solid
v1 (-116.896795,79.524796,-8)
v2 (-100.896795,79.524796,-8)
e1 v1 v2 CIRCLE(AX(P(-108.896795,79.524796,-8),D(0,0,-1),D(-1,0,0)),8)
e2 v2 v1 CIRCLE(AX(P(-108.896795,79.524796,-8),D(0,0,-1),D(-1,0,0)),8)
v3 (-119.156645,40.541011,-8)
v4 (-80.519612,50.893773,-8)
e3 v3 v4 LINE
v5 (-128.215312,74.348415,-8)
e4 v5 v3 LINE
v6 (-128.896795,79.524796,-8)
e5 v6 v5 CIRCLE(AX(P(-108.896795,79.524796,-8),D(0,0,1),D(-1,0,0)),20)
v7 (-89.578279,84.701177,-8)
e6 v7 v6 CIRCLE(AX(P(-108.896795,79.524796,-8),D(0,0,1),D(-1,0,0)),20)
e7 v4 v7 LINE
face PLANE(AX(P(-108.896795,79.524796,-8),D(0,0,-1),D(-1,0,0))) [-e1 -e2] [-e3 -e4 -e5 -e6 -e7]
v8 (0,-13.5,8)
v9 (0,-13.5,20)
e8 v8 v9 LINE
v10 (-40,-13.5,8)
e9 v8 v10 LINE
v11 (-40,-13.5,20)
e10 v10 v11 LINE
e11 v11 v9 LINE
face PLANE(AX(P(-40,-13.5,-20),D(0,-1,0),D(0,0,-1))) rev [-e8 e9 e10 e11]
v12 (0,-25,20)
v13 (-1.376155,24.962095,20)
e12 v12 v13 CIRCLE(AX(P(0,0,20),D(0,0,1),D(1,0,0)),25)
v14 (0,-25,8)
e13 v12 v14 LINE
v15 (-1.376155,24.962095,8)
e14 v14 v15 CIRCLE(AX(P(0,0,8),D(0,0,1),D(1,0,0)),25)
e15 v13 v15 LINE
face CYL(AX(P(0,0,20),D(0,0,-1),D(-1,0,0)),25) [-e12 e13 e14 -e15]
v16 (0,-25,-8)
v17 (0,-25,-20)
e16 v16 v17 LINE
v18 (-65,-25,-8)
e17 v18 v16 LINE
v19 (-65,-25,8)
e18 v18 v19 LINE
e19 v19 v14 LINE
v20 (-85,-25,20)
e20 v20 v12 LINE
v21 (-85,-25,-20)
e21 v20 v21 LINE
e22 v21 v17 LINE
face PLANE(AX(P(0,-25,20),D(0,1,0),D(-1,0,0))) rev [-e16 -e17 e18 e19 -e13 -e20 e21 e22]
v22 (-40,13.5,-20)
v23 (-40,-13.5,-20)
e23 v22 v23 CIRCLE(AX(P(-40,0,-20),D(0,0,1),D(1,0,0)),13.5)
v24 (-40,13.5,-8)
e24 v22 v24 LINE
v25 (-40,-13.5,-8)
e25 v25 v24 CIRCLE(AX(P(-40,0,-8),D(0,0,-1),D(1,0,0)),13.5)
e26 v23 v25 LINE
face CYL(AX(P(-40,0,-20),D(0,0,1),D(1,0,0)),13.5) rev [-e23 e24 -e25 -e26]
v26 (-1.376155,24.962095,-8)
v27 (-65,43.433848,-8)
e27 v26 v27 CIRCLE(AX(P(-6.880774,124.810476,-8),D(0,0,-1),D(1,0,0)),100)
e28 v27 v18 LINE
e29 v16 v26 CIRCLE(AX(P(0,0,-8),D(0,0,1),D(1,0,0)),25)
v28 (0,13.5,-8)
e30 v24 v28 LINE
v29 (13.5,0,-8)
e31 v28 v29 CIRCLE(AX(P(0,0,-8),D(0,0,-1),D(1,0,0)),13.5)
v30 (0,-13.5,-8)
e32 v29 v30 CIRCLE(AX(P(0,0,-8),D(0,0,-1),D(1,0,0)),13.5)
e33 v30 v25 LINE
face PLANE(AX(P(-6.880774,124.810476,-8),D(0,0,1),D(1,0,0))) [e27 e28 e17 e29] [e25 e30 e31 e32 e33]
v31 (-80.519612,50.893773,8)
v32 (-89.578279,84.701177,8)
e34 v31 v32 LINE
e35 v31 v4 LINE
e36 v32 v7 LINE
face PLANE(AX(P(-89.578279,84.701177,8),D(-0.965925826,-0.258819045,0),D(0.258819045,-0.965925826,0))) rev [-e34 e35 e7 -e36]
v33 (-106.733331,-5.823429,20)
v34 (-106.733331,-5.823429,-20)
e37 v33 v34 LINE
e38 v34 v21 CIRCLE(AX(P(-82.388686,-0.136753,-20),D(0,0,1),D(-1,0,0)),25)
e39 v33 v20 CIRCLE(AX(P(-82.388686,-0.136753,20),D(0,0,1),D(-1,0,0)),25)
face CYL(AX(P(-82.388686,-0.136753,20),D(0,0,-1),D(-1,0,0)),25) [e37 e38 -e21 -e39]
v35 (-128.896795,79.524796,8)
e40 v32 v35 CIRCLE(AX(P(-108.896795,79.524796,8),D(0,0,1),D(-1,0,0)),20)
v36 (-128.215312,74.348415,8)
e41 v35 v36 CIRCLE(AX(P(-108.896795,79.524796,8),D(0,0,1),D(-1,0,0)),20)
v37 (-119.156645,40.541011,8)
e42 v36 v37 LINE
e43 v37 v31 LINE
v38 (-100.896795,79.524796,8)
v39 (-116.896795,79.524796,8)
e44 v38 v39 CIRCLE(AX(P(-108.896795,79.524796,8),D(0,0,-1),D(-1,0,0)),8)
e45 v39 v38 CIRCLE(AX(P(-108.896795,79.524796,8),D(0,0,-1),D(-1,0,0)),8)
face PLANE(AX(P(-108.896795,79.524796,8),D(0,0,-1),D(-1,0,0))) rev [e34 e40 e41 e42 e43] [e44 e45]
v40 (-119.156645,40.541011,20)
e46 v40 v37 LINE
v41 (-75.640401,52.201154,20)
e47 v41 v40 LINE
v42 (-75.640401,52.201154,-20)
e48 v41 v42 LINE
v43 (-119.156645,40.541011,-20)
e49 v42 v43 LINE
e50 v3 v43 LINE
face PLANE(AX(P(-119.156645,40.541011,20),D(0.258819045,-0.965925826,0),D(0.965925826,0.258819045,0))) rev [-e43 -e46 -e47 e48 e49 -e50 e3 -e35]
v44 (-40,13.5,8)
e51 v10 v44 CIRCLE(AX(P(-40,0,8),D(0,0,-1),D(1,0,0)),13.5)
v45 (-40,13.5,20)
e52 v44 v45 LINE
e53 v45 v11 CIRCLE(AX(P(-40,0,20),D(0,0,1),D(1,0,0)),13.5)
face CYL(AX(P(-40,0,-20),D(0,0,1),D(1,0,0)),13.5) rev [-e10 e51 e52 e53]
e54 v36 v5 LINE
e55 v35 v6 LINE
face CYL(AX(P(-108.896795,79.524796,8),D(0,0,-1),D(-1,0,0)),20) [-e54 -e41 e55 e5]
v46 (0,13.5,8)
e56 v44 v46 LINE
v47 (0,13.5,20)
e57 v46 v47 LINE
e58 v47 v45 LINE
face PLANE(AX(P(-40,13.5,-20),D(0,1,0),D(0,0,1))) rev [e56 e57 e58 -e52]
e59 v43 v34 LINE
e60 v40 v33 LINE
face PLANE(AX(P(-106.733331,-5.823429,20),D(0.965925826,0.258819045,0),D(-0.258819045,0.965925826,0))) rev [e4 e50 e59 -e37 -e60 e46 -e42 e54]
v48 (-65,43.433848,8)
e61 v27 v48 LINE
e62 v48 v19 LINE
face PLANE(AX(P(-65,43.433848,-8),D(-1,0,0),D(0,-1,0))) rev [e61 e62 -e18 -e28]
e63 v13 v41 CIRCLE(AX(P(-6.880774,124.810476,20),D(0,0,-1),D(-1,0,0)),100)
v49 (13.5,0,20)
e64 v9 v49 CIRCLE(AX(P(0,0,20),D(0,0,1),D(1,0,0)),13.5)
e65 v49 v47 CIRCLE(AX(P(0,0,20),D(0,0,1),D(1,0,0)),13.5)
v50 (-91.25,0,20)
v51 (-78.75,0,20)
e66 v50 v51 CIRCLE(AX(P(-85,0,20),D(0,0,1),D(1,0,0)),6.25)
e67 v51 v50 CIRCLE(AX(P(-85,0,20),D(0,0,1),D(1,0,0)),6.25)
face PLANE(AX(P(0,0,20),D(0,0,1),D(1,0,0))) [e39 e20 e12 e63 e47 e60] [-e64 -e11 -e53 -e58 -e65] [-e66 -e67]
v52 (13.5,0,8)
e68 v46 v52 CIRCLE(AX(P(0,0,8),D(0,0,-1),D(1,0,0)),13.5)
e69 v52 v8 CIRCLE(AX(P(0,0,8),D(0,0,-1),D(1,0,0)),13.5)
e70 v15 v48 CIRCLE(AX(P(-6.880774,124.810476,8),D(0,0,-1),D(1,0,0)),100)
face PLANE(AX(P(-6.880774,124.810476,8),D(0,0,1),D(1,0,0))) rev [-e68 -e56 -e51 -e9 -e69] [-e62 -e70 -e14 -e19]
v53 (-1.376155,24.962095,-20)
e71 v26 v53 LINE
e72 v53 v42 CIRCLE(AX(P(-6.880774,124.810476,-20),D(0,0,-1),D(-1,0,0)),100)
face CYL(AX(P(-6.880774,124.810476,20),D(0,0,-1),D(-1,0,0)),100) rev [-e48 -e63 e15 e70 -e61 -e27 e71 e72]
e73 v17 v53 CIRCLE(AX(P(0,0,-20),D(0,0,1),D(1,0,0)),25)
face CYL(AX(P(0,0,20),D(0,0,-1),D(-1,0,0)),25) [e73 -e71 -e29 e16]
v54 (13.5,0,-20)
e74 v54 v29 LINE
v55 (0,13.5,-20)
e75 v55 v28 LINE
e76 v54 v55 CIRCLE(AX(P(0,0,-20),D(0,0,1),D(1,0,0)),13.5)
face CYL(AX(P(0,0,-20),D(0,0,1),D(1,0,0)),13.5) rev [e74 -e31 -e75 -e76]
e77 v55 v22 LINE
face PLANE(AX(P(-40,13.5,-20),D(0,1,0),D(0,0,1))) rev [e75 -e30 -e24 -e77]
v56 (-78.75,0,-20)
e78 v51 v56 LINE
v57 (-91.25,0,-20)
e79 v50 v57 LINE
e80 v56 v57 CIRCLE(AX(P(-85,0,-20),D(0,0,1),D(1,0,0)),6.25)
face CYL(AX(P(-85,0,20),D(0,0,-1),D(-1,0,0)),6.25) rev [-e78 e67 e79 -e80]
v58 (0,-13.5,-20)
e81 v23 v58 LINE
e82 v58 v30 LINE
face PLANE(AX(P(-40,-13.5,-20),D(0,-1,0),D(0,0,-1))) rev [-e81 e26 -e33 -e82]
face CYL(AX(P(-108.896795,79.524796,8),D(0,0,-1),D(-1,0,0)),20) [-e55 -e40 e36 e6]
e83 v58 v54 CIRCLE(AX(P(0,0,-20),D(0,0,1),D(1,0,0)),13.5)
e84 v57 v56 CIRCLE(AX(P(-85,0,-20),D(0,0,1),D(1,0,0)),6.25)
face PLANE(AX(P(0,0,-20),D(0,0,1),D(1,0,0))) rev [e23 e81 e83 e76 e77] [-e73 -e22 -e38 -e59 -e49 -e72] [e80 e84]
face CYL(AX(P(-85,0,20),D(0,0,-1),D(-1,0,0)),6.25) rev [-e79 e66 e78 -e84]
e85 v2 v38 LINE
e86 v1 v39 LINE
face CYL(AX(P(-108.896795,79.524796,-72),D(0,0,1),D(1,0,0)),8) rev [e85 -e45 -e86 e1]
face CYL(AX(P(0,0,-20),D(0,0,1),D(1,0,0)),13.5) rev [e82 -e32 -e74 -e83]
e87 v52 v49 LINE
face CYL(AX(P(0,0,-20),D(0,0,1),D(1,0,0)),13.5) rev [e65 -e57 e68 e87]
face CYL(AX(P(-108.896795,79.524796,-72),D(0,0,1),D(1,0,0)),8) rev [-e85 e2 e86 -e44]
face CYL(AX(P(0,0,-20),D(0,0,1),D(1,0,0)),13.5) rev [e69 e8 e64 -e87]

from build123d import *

# Parameters (mm, degrees)
BASE_PLATE_PROFILE_R = 6.25
BASE_PLATE_DEPTH     = 20
GUIDE_SLOT_DEPTH     = 137.100207792
FORK_GAP_16MM_DEPTH  = 8
PIVOT_LUG_DEPTH      = 8
PIVOT_HOLE_PROFILE_R = 8
PIVOT_HOLE_16_DEPTH  = 80


with BuildPart() as part:
    # Base Plate Profile → Base Plate (new, symmetric)
    with BuildSketch(Plane.XY):
        with BuildLine():
            Line((0, -25), (-85, -25))
            ThreePointArc((-85, -25), (-98.929277245, -18.882655563), (-106.733331092, -5.823428515))
            Line((-106.733331092, -5.823428515), (-119.156645256, 40.541011147))
            Line((-119.156645256, 40.541011147), (-75.640400658, 52.201153745))
            ThreePointArc((-75.640400658, 52.201153745), (-41.316083866, 30.926455065), (-1.376154737, 24.962095227))
            ThreePointArc((-1.376154737, 24.962095227), (24.99052201, 0.688338331), (0, -25))
        make_face()
        with Locations((-85, 0)):
            Circle(BASE_PLATE_PROFILE_R, mode=Mode.SUBTRACT)
    extrude(amount=BASE_PLATE_DEPTH, both=True)

    # Guide Slot Profile → Guide Slot (cut, through all)
    with BuildSketch(Plane.XY.offset(20)):
        with BuildLine():
            Line((-40, 13.5), (0, 13.5))
            ThreePointArc((0, 13.5), (13.5, 0), (0, -13.5))
            Line((0, -13.5), (-40, -13.5))
            ThreePointArc((-40, -13.5), (-53.5, 0), (-40, 13.5))
        make_face()
    extrude(amount=-GUIDE_SLOT_DEPTH, mode=Mode.SUBTRACT)

    # Fork Gap Profile → Fork Gap 16mm (cut, symmetric)
    with BuildSketch(Plane.XY):
        with BuildLine():
            Line((-65, 43.433848458), (-65, -25))
            Line((-65, -25), (0, -25))
            ThreePointArc((0, -25), (24.99052201, 0.688338331), (-1.376154737, 24.962095227))
            ThreePointArc((-1.376154737, 24.962095227), (-34.762230676, 28.775980481), (-65, 43.433848458))
        make_face()
    extrude(amount=FORK_GAP_16MM_DEPTH, both=True, mode=Mode.SUBTRACT)

    # Pivot Lug Profile → Pivot Lug (add, symmetric)
    with BuildSketch(Plane.XY):
        with BuildLine():
            Line((-119.156645256, 40.541011147), (-128.215311835, 74.348415067))
            ThreePointArc((-128.215311835, 74.348415067), (-114.073176211, 98.843312495), (-89.578278783, 84.701176871))
            Line((-89.578278783, 84.701176871), (-80.519612205, 50.893772951))
            Line((-80.519612205, 50.893772951), (-119.156645256, 40.541011147))
        make_face()
    extrude(amount=PIVOT_LUG_DEPTH, both=True)

    # Pivot Hole Profile → Pivot Hole Ø16 (cut, symmetric)
    with BuildSketch(Plane.XY.offset(8)):
        with Locations(Location((-108.896795309, 79.524795969, 0), (0, 0, 180))):
            Circle(PIVOT_HOLE_PROFILE_R)
    extrude(amount=PIVOT_HOLE_16_DEPTH, both=True, mode=Mode.SUBTRACT)


solid = part.part
